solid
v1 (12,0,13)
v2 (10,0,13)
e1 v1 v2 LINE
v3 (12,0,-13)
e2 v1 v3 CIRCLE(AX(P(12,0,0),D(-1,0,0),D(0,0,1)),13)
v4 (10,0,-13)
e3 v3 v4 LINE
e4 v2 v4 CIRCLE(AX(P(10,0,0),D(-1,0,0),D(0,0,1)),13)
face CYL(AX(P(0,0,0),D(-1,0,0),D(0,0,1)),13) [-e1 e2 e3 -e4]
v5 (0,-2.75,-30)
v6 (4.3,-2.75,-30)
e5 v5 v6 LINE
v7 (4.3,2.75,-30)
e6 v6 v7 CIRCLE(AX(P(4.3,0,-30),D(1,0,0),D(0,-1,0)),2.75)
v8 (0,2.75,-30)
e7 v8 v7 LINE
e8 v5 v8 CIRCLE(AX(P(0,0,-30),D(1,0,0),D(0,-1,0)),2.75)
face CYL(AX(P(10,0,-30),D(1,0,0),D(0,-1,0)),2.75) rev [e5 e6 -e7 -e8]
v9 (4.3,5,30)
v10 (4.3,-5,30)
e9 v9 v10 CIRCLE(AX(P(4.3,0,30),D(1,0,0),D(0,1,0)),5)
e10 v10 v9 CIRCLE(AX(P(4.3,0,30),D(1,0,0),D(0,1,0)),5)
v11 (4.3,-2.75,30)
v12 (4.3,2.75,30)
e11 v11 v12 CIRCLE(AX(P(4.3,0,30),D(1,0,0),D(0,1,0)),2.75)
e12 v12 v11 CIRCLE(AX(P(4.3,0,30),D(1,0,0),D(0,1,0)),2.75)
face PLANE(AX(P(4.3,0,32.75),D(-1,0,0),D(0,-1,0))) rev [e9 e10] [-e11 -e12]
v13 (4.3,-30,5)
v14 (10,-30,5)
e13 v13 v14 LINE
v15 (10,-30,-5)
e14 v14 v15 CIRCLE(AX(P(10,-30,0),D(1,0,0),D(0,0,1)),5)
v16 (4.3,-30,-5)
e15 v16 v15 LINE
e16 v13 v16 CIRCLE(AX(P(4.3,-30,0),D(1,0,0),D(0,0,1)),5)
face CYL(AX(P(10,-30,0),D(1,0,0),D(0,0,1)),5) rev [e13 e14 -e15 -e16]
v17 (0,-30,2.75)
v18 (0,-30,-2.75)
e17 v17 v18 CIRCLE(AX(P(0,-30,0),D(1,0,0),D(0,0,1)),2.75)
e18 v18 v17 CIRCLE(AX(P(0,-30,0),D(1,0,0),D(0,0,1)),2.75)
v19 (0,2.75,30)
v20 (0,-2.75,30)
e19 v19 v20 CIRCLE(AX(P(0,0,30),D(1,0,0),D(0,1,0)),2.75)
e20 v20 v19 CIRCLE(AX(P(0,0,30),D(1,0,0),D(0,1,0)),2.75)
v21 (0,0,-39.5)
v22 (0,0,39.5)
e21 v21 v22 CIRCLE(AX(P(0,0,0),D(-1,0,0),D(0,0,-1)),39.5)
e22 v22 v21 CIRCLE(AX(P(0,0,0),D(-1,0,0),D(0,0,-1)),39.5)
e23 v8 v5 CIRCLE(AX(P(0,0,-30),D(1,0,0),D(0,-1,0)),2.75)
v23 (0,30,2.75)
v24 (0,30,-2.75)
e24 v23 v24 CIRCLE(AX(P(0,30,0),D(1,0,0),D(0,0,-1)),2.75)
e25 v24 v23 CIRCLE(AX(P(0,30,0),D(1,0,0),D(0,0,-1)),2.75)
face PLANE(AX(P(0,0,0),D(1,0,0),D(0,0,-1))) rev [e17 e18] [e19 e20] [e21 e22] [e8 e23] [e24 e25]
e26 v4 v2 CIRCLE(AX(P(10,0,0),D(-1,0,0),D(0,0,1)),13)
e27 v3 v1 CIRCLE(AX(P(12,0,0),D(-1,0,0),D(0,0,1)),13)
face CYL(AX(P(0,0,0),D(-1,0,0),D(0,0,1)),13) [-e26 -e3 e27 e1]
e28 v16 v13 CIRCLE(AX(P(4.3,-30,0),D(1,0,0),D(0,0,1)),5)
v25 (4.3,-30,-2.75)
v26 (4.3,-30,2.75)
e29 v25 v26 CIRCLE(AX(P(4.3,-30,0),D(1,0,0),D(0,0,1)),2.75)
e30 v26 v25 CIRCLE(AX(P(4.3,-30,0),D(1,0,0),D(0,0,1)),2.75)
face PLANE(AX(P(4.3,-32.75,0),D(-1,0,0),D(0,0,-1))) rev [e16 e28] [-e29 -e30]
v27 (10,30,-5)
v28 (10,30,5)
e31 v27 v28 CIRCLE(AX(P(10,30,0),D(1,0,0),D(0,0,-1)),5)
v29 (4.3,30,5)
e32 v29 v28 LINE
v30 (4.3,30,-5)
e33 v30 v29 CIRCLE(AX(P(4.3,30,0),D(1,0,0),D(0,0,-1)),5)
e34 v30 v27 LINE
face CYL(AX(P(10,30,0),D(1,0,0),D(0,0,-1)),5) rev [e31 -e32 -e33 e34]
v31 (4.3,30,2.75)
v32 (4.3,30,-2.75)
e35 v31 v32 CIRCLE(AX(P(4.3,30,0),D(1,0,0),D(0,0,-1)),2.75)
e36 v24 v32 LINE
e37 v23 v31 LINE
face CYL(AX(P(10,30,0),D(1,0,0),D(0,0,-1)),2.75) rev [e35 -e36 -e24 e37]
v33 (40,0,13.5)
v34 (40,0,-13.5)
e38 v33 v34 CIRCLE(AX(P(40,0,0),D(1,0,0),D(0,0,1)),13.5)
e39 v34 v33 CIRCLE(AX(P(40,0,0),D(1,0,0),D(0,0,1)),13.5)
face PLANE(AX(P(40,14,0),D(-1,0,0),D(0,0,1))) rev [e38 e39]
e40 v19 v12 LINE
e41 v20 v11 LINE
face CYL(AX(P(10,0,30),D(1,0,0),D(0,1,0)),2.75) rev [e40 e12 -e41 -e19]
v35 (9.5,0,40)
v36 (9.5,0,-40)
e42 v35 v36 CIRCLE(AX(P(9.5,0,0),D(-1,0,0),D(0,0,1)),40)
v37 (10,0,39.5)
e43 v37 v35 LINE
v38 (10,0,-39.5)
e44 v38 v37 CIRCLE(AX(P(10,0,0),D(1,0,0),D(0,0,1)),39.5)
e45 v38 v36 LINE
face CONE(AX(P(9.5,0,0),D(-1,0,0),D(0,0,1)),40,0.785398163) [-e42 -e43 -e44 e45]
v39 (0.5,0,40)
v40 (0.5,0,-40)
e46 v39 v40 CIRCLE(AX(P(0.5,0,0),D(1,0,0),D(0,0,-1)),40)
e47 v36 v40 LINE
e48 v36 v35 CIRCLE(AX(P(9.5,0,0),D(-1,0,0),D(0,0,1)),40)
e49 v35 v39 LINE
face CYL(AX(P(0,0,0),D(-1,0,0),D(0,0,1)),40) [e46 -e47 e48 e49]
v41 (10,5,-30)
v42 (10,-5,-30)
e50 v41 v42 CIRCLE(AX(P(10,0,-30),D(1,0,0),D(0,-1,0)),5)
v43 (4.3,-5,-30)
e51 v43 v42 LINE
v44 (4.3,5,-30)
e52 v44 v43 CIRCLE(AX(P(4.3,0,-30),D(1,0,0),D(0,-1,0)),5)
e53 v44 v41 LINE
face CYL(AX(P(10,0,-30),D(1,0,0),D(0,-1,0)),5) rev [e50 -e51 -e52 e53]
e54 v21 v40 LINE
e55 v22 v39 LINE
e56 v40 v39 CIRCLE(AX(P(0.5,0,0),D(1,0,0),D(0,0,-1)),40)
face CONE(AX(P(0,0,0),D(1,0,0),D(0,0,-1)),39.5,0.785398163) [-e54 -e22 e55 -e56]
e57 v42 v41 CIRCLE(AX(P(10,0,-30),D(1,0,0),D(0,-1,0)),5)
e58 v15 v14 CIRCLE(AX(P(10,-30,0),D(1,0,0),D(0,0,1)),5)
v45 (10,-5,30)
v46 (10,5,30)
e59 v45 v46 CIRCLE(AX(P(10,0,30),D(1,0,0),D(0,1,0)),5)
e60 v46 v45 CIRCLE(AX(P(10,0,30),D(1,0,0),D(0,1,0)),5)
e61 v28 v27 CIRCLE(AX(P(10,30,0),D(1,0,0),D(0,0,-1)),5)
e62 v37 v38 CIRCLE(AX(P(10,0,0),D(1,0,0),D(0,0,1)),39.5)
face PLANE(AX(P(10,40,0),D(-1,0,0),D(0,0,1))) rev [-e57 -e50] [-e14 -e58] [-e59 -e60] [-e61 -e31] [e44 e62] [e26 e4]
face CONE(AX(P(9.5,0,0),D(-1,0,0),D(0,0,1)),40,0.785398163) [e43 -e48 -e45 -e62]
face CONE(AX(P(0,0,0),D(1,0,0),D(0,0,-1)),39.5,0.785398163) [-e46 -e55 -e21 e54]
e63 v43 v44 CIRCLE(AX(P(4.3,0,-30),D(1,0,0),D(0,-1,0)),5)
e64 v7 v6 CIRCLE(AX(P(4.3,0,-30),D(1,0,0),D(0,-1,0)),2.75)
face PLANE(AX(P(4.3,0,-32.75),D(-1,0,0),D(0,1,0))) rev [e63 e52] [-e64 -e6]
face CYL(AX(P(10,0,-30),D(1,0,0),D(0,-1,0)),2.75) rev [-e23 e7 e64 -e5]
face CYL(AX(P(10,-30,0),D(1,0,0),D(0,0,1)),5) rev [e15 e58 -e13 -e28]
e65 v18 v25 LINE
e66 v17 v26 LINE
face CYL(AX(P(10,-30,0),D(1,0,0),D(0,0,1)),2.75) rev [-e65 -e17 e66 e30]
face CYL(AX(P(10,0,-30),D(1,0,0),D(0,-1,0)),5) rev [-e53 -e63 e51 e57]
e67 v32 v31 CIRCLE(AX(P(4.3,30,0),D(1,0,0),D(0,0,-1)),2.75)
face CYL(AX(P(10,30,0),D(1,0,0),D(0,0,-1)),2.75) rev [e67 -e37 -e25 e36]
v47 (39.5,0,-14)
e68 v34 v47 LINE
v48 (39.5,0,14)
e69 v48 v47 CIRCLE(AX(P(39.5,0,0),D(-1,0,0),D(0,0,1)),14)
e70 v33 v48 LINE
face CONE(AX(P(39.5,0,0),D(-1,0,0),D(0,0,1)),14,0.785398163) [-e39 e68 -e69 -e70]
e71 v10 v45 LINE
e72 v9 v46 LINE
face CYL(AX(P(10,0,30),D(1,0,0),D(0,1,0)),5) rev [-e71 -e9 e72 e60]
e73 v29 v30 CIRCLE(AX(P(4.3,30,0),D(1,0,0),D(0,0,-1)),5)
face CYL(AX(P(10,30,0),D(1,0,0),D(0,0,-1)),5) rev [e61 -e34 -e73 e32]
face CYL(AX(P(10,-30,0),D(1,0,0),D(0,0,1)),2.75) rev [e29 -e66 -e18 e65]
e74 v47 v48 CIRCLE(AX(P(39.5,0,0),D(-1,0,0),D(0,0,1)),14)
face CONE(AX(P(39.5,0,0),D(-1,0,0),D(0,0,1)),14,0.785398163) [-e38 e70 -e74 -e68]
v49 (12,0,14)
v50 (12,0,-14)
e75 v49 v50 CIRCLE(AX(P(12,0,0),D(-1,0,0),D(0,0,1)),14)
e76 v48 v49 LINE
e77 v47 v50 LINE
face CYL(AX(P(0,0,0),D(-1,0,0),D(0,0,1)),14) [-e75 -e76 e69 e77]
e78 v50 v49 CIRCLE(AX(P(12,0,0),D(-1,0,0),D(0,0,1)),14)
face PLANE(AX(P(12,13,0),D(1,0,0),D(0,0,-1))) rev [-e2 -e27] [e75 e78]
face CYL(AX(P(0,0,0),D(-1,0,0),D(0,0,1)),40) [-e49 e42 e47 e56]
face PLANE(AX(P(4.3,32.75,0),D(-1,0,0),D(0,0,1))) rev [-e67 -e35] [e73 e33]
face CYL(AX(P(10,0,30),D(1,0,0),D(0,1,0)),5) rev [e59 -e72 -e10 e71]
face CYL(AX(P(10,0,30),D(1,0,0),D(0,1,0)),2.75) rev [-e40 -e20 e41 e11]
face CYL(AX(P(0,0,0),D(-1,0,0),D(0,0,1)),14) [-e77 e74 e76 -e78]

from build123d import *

# Parameters (mm, degrees)
CHAMFER_1_SIZE           = 0.5
PATTERN_CIRCULAR_1_COUNT = 4


with BuildPart() as part:
    # 草图2 → 旋转1 (revolve)
    with BuildSketch(Plane.XY, mode=Mode.PRIVATE) as revolve_1_sk:
        Polygon((0, 0), (0, 40), (10, 40), (10, 13), (12, 13), (12, 14), (40, 14), (40, 0), align=None)
    revolve(revolve_1_sk.sketch.rotate(Axis((0, 0, 0), (1, 0, 0)), 90), axis=Axis((0, 0, 0), (1, 0, 0)))

    # 倒角1
    chamfer_1_edges = [part.edges().sort_by_distance(p)[0] for p in [
        (40, 0, -14),
        (10, 0, -40),
        (0, 0, -40),
    ]]
    chamfer(chamfer_1_edges, length=CHAMFER_1_SIZE)

    # 草图7 → 打孔尺寸(%根据)内六角圆柱头螺钉的类型1 (revolve, cut)
    with BuildSketch(Plane(origin=(10, 30, 0), x_dir=(0, 0, -1), z_dir=(0, 1, 0))):
        Polygon((0, 0), (0, 13.152366702), (2.75, 11.5), (2.75, 5.7), (5, 5.7), (5, 0), align=None)
    hole_wizard_1 = revolve(axis=Axis((16.35, 30, 0), (-1, 0, 0)), mode=Mode.SUBTRACT)

    # 阵列(圆周)1: 打孔尺寸(%根据)内六角圆柱头螺钉的类型1 ×4 about axis
    pattern_circular_1_axis = Axis((0, 0, 0), (1, 0, 0))
    for i in range(1, PATTERN_CIRCULAR_1_COUNT):
        add(hole_wizard_1.rotate(pattern_circular_1_axis, i * 360 / PATTERN_CIRCULAR_1_COUNT), mode=Mode.SUBTRACT)


solid = part.part
